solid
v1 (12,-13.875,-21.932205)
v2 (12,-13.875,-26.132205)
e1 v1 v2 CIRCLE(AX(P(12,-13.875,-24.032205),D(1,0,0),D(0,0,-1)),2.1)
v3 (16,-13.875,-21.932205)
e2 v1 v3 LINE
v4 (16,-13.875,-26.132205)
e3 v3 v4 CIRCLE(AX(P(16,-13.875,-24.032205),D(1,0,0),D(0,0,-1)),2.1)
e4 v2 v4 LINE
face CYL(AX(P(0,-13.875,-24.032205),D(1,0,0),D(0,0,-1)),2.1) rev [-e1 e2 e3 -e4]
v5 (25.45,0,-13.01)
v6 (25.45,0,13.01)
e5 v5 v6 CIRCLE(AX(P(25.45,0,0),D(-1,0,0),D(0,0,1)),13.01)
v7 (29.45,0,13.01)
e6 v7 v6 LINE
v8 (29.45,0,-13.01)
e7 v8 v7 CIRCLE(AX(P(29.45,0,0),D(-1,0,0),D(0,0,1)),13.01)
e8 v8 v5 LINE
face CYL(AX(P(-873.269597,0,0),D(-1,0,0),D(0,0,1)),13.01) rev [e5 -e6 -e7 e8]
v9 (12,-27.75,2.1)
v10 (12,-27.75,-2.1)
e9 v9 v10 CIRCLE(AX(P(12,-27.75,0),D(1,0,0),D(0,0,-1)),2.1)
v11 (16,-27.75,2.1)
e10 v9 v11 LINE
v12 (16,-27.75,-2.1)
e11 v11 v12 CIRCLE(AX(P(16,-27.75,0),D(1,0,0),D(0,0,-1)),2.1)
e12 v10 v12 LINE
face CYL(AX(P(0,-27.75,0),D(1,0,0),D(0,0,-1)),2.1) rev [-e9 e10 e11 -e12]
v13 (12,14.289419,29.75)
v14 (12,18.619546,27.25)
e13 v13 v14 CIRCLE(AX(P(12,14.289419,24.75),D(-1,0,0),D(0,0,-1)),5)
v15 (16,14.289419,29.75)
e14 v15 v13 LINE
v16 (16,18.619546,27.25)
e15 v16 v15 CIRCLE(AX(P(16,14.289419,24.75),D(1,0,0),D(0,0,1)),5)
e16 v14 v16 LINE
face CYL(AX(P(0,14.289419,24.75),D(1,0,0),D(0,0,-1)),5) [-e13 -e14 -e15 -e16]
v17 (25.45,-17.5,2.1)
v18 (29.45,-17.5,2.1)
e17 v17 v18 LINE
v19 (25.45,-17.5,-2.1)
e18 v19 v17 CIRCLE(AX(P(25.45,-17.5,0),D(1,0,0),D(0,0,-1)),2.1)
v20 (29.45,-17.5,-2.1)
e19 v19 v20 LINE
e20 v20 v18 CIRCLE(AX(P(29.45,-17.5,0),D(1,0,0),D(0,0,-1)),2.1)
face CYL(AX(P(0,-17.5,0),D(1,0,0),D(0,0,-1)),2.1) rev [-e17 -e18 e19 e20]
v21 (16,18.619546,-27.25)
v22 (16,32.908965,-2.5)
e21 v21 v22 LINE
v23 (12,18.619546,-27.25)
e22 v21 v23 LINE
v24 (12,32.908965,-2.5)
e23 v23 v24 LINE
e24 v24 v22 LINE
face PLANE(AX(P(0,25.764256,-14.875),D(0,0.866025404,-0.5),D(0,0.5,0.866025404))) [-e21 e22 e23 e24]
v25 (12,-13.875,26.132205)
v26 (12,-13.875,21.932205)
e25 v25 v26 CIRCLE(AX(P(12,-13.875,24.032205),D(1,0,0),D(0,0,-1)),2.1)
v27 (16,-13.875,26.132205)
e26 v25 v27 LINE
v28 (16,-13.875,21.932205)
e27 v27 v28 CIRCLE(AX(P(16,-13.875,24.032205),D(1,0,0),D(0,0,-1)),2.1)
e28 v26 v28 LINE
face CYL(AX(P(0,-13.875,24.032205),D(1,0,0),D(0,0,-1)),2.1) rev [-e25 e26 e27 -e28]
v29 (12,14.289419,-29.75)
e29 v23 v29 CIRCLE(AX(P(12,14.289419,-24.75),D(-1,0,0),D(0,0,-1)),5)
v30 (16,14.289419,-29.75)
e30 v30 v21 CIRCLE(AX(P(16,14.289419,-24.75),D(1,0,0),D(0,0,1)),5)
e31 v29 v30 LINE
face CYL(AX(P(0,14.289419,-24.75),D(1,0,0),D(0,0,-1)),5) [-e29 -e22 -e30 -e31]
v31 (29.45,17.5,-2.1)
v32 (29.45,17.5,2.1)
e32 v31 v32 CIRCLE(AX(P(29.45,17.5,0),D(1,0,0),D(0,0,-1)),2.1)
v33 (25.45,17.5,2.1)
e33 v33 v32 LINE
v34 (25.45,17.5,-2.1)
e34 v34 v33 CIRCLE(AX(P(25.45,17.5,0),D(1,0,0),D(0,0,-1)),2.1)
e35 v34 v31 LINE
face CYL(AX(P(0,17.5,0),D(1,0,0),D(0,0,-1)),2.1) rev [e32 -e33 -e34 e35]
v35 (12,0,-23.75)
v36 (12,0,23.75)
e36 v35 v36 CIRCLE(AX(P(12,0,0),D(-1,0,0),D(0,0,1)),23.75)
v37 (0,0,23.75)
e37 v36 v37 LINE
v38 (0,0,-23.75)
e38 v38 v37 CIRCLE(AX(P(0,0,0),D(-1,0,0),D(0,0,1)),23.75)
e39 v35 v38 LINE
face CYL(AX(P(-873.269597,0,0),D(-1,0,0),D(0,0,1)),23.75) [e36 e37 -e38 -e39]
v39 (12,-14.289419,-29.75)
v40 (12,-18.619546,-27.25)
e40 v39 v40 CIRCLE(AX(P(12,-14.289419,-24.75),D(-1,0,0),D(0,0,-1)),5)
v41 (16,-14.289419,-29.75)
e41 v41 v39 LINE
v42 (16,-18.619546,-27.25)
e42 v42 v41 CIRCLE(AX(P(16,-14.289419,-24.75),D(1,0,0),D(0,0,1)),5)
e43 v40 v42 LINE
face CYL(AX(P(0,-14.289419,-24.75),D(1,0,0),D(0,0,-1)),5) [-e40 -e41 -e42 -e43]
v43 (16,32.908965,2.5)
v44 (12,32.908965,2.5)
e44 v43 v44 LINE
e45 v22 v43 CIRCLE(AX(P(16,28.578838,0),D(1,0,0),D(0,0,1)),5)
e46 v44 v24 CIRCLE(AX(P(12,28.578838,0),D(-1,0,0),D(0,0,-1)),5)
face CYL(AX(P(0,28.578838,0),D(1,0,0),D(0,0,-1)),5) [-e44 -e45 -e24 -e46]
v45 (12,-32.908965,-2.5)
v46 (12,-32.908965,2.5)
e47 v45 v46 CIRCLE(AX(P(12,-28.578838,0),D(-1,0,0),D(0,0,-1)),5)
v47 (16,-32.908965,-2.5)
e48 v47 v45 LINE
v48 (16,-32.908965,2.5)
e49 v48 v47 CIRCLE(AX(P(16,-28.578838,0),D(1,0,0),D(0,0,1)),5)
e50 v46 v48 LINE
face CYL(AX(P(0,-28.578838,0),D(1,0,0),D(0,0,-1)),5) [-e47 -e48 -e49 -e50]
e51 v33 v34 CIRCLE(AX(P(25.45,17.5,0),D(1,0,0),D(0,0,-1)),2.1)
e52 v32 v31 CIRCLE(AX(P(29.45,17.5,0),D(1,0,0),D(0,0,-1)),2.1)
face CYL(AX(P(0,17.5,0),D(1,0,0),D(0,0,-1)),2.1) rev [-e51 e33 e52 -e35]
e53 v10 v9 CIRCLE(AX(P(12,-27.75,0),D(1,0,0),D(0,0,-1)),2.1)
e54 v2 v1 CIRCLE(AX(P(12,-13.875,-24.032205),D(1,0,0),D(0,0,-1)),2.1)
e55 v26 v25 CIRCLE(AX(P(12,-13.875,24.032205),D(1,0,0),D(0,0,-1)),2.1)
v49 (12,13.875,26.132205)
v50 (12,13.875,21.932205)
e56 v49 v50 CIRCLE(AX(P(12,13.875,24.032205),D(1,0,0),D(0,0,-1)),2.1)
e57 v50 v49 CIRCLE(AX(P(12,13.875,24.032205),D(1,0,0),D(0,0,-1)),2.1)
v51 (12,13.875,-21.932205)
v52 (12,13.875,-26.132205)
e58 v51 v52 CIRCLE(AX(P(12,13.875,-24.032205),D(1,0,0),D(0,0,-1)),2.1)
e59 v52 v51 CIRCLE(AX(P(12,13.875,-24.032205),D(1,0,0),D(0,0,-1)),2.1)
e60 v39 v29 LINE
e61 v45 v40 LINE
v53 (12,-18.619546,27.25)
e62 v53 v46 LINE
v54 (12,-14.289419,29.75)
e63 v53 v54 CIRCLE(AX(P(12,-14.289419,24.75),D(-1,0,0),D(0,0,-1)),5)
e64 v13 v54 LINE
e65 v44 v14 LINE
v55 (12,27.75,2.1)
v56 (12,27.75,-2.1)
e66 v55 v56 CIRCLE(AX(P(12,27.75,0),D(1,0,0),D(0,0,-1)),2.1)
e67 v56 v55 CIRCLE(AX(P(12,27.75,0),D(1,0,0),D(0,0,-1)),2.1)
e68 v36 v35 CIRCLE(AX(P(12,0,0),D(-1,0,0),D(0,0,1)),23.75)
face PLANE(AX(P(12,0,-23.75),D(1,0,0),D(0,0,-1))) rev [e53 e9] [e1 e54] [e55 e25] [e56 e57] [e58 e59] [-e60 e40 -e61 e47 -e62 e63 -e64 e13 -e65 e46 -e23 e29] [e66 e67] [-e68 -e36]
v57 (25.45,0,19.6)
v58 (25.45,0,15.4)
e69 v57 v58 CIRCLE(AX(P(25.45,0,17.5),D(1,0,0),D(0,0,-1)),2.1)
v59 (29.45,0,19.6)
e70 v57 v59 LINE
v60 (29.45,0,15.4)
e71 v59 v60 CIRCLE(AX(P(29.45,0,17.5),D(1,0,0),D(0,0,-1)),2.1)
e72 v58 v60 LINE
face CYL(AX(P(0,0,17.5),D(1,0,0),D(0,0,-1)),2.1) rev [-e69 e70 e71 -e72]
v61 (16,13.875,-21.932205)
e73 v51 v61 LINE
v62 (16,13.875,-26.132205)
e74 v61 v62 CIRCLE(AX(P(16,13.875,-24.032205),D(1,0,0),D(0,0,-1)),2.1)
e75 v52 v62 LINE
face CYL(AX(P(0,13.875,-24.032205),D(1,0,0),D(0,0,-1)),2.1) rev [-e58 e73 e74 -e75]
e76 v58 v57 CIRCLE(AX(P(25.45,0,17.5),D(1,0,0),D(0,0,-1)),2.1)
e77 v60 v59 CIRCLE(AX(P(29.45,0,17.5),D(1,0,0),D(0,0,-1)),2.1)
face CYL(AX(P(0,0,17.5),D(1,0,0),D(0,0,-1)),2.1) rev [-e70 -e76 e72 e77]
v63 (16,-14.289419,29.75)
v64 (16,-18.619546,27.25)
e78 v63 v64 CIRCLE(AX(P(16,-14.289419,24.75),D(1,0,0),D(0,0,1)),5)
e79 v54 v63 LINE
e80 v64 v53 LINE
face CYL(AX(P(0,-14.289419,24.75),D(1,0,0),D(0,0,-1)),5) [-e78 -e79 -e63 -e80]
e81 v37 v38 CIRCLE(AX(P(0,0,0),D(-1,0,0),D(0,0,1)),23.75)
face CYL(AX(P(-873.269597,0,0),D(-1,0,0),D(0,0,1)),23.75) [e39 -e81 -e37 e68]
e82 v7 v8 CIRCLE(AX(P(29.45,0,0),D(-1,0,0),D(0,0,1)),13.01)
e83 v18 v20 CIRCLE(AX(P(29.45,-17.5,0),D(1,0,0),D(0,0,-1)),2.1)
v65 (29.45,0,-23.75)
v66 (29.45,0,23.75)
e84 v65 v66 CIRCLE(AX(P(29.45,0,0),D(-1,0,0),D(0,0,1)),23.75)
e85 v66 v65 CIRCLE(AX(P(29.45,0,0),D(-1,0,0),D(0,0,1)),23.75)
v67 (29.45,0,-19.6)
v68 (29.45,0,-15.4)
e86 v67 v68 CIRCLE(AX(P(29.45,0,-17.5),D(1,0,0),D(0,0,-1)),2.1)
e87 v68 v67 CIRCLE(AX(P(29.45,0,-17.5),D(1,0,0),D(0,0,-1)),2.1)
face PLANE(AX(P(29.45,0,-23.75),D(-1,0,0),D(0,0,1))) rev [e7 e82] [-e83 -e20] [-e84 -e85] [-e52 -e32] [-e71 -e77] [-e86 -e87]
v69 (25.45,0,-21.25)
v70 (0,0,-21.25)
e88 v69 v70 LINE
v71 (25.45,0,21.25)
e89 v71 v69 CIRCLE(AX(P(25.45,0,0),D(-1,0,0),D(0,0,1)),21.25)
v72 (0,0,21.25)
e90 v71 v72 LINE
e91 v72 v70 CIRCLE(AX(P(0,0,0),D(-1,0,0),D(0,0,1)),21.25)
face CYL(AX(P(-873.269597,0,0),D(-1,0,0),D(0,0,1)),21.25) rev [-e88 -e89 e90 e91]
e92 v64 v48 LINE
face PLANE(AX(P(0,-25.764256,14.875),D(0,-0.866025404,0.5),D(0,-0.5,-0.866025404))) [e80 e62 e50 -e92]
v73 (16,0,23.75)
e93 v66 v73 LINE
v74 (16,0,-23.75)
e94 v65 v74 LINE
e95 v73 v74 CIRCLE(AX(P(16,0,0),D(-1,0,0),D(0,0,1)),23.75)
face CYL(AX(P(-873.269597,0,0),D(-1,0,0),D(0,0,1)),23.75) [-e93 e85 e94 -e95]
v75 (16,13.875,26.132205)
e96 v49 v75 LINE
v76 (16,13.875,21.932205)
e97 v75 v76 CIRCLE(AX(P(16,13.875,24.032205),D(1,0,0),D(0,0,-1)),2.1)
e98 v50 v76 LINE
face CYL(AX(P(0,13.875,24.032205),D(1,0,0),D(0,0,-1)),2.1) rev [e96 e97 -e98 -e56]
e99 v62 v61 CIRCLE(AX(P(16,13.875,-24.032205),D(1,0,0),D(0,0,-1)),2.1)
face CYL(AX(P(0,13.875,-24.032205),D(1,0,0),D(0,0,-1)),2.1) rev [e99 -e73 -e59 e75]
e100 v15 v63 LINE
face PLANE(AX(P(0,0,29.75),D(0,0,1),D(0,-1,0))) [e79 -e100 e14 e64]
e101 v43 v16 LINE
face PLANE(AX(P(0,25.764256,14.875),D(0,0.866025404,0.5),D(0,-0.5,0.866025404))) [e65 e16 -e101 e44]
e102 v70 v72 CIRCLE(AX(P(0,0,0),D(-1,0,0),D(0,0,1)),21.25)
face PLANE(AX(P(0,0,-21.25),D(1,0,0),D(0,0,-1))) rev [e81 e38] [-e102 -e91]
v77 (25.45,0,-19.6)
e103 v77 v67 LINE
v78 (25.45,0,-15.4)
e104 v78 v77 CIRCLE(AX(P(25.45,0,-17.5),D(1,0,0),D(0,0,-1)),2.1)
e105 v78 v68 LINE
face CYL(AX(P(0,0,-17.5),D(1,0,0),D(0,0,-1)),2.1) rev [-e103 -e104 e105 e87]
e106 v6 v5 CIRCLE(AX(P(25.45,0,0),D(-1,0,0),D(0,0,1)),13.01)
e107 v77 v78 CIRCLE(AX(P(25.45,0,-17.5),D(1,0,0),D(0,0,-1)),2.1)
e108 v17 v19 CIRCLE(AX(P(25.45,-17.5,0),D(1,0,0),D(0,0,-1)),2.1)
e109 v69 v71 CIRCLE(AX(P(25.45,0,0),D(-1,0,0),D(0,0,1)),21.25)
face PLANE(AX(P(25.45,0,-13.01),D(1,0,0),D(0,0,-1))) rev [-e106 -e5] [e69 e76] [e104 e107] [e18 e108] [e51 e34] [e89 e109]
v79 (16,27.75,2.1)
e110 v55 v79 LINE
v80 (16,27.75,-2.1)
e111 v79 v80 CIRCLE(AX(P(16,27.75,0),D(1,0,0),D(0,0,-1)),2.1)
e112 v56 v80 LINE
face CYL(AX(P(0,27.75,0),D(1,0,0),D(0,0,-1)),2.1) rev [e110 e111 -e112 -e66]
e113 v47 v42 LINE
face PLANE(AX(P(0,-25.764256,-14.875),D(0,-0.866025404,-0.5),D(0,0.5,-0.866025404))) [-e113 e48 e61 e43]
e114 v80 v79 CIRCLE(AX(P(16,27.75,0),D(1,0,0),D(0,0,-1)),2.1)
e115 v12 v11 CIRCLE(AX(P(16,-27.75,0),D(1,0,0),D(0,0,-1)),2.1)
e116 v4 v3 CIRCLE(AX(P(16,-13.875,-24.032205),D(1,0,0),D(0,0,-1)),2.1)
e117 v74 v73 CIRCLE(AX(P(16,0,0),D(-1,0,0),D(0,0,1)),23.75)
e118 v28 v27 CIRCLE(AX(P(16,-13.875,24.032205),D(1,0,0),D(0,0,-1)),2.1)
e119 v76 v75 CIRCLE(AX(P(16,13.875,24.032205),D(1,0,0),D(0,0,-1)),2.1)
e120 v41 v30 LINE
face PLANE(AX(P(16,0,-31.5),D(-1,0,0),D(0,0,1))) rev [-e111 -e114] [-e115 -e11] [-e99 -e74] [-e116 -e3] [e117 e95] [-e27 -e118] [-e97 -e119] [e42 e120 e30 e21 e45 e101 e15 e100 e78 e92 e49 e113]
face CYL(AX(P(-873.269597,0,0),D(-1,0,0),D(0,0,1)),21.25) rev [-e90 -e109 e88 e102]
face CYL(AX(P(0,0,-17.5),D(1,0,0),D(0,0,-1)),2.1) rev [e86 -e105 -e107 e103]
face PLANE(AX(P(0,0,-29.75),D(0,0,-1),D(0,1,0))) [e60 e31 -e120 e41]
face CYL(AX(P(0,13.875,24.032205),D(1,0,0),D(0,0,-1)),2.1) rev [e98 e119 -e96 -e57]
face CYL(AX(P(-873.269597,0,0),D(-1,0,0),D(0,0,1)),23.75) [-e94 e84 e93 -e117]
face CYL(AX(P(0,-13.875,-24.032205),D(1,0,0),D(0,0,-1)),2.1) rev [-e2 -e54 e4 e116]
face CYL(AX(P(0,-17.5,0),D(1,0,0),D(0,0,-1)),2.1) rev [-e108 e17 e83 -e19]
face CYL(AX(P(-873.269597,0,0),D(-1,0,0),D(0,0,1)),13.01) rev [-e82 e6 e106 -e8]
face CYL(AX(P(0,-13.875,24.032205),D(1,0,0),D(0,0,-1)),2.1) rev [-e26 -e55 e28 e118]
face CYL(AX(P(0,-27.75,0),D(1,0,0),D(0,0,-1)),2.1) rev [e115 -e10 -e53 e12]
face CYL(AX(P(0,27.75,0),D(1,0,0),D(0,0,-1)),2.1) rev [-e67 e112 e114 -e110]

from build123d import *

# Parameters (mm, degrees)
SKETCH_2_R          = 2.1
CUT_EXTRUDE_1_DEPTH = 48.333920184
SKETCH_3_R          = 2.1
CUT_EXTRUDE_2_DEPTH = 53.389073288
EXTRUDE_1_DEPTH     = 4
FILLET_1_R          = 5


with BuildPart() as part:
    # 草图1 → 旋转1 (revolve)
    with BuildSketch(Plane(origin=(0, 0, 0), x_dir=(1, 0, 0), z_dir=(0, 1, 0)), mode=Mode.PRIVATE) as revolve_1_sk:
        Polygon((0, 21.25), (0, 23.75), (12, 23.75), (12, 31.5), (16, 31.5), (16, 23.75), (29.45, 23.75), (29.45, 13.01), (25.45, 13.01), (25.45, 21.25), align=None)
    revolve(revolve_1_sk.sketch.rotate(Axis((-873.269597079, 0, 0), (1, 0, 0)), 180), axis=Axis((-873.269597079, 0, 0), (1, 0, 0)))

    # 草图2 → 切除-拉伸1 (cut, through all)
    with BuildSketch(Plane(origin=(16, 0, 0), x_dir=(0, 0, -1), z_dir=(1, 0, 0))):
        with Locations((0, 27.75)):
            Circle(SKETCH_2_R)
        with Locations((-24.032204955, 13.875)):
            Circle(SKETCH_2_R)
        with Locations((-24.032204955, -13.875)):
            Circle(SKETCH_2_R)
        with Locations((0, -27.75)):
            Circle(SKETCH_2_R)
        with Locations((24.032204955, -13.875)):
            Circle(SKETCH_2_R)
        with Locations((24.032204955, 13.875)):
            Circle(SKETCH_2_R)
        with BuildLine():
            ThreePointArc((31.5, 0), (31.059418861, 5.25), (29.75, 10.35313962))
            Line((29.75, 10.35313962), (29.75, -10.35313962))
            ThreePointArc((29.75, -10.35313962), (31.059418861, -5.25), (31.5, 0))
        make_face()
        with BuildLine():
            ThreePointArc((23.84108192, 20.587685952), (15.75, 27.279800219), (5.90891808, 30.940825573))
            Line((5.90891808, 30.940825573), (23.84108192, 20.587685952))
        make_face()
        with BuildLine():
            Line((-23.84108192, 20.587685952), (-5.90891808, 30.940825573))
            ThreePointArc((-5.90891808, 30.940825573), (-15.75, 27.279800219), (-23.84108192, 20.587685952))
        make_face()
        with BuildLine():
            Line((-29.75, -10.35313962), (-29.75, 10.35313962))
            ThreePointArc((-29.75, 10.35313962), (-31.5, 0), (-29.75, -10.35313962))
        make_face()
        with BuildLine():
            Line((-5.90891808, -30.940825573), (-23.84108192, -20.587685952))
            ThreePointArc((-23.84108192, -20.587685952), (-15.75, -27.279800219), (-5.90891808, -30.940825573))
        make_face()
        with BuildLine():
            ThreePointArc((5.90891808, -30.940825573), (15.75, -27.279800219), (23.84108192, -20.587685952))
            Line((23.84108192, -20.587685952), (5.90891808, -30.940825573))
        make_face()
    extrude(amount=-CUT_EXTRUDE_1_DEPTH, mode=Mode.SUBTRACT)

    # 草图3 → 切除-拉伸2 (cut, through all)
    with BuildSketch(Plane(origin=(29.45, 0, 0), x_dir=(0, 0, -1), z_dir=(1, 0, 0))):
        with Locations((0, 17.5)):
            Circle(SKETCH_3_R)
        with Locations((17.5, 0)):
            Circle(SKETCH_3_R)
        with Locations((0, -17.5)):
            Circle(SKETCH_3_R)
        with Locations((-17.5, 0)):
            Circle(SKETCH_3_R)
    extrude(amount=-CUT_EXTRUDE_2_DEPTH, mode=Mode.SUBTRACT)

    # 草图2<3> → 凸台-拉伸1 (add)
    with BuildSketch(Plane(origin=(16, 0, 0), x_dir=(0, 0, -1), z_dir=(1, 0, 0))):
        with BuildLine():
            ThreePointArc((-29.75, 10.35313962), (-27.279800219, 15.75), (-23.84108192, 20.587685952))
            Line((-23.84108192, 20.587685952), (-29.75, 17.176170508))
            Line((-29.75, 17.176170508), (-29.75, 10.35313962))
        make_face()
        with BuildLine():
            Line((5.90891808, 30.940825573), (0, 34.352341017))
            Line((0, 34.352341017), (-5.90891808, 30.940825573))
            ThreePointArc((-5.90891808, 30.940825573), (0, 31.5), (5.90891808, 30.940825573))
        make_face()
        with BuildLine():
            Line((29.75, 17.176170508), (23.84108192, 20.587685952))
            ThreePointArc((23.84108192, 20.587685952), (27.279800219, 15.75), (29.75, 10.35313962))
            Line((29.75, 10.35313962), (29.75, 17.176170508))
        make_face()
        with BuildLine():
            Line((29.75, -17.176170508), (29.75, -10.35313962))
            ThreePointArc((29.75, -10.35313962), (27.279800219, -15.75), (23.84108192, -20.587685952))
            Line((23.84108192, -20.587685952), (29.75, -17.176170508))
        make_face()
        with BuildLine():
            ThreePointArc((5.90891808, -30.940825573), (0, -31.5), (-5.90891808, -30.940825573))
            Line((-5.90891808, -30.940825573), (0, -34.352341017))
            Line((0, -34.352341017), (5.90891808, -30.940825573))
        make_face()
        with BuildLine():
            ThreePointArc((-23.84108192, -20.587685952), (-27.279800219, -15.75), (-29.75, -10.35313962))
            Line((-29.75, -10.35313962), (-29.75, -17.176170508))
            Line((-29.75, -17.176170508), (-23.84108192, -20.587685952))
        make_face()
    extrude(amount=-EXTRUDE_1_DEPTH)

    # 圆角1
    fillet_1_edges = [part.edges().sort_by_distance(p)[0] for p in [
        (14, -17.176170508, 29.75),
        (14, -34.352341017, 0),
        (14, -17.176170508, -29.75),
        (14, 17.176170508, -29.75),
        (14, 34.352341017, 0),
        (14, 17.176170508, 29.75),
    ]]
    fillet(fillet_1_edges, radius=FILLET_1_R)


solid = part.part
